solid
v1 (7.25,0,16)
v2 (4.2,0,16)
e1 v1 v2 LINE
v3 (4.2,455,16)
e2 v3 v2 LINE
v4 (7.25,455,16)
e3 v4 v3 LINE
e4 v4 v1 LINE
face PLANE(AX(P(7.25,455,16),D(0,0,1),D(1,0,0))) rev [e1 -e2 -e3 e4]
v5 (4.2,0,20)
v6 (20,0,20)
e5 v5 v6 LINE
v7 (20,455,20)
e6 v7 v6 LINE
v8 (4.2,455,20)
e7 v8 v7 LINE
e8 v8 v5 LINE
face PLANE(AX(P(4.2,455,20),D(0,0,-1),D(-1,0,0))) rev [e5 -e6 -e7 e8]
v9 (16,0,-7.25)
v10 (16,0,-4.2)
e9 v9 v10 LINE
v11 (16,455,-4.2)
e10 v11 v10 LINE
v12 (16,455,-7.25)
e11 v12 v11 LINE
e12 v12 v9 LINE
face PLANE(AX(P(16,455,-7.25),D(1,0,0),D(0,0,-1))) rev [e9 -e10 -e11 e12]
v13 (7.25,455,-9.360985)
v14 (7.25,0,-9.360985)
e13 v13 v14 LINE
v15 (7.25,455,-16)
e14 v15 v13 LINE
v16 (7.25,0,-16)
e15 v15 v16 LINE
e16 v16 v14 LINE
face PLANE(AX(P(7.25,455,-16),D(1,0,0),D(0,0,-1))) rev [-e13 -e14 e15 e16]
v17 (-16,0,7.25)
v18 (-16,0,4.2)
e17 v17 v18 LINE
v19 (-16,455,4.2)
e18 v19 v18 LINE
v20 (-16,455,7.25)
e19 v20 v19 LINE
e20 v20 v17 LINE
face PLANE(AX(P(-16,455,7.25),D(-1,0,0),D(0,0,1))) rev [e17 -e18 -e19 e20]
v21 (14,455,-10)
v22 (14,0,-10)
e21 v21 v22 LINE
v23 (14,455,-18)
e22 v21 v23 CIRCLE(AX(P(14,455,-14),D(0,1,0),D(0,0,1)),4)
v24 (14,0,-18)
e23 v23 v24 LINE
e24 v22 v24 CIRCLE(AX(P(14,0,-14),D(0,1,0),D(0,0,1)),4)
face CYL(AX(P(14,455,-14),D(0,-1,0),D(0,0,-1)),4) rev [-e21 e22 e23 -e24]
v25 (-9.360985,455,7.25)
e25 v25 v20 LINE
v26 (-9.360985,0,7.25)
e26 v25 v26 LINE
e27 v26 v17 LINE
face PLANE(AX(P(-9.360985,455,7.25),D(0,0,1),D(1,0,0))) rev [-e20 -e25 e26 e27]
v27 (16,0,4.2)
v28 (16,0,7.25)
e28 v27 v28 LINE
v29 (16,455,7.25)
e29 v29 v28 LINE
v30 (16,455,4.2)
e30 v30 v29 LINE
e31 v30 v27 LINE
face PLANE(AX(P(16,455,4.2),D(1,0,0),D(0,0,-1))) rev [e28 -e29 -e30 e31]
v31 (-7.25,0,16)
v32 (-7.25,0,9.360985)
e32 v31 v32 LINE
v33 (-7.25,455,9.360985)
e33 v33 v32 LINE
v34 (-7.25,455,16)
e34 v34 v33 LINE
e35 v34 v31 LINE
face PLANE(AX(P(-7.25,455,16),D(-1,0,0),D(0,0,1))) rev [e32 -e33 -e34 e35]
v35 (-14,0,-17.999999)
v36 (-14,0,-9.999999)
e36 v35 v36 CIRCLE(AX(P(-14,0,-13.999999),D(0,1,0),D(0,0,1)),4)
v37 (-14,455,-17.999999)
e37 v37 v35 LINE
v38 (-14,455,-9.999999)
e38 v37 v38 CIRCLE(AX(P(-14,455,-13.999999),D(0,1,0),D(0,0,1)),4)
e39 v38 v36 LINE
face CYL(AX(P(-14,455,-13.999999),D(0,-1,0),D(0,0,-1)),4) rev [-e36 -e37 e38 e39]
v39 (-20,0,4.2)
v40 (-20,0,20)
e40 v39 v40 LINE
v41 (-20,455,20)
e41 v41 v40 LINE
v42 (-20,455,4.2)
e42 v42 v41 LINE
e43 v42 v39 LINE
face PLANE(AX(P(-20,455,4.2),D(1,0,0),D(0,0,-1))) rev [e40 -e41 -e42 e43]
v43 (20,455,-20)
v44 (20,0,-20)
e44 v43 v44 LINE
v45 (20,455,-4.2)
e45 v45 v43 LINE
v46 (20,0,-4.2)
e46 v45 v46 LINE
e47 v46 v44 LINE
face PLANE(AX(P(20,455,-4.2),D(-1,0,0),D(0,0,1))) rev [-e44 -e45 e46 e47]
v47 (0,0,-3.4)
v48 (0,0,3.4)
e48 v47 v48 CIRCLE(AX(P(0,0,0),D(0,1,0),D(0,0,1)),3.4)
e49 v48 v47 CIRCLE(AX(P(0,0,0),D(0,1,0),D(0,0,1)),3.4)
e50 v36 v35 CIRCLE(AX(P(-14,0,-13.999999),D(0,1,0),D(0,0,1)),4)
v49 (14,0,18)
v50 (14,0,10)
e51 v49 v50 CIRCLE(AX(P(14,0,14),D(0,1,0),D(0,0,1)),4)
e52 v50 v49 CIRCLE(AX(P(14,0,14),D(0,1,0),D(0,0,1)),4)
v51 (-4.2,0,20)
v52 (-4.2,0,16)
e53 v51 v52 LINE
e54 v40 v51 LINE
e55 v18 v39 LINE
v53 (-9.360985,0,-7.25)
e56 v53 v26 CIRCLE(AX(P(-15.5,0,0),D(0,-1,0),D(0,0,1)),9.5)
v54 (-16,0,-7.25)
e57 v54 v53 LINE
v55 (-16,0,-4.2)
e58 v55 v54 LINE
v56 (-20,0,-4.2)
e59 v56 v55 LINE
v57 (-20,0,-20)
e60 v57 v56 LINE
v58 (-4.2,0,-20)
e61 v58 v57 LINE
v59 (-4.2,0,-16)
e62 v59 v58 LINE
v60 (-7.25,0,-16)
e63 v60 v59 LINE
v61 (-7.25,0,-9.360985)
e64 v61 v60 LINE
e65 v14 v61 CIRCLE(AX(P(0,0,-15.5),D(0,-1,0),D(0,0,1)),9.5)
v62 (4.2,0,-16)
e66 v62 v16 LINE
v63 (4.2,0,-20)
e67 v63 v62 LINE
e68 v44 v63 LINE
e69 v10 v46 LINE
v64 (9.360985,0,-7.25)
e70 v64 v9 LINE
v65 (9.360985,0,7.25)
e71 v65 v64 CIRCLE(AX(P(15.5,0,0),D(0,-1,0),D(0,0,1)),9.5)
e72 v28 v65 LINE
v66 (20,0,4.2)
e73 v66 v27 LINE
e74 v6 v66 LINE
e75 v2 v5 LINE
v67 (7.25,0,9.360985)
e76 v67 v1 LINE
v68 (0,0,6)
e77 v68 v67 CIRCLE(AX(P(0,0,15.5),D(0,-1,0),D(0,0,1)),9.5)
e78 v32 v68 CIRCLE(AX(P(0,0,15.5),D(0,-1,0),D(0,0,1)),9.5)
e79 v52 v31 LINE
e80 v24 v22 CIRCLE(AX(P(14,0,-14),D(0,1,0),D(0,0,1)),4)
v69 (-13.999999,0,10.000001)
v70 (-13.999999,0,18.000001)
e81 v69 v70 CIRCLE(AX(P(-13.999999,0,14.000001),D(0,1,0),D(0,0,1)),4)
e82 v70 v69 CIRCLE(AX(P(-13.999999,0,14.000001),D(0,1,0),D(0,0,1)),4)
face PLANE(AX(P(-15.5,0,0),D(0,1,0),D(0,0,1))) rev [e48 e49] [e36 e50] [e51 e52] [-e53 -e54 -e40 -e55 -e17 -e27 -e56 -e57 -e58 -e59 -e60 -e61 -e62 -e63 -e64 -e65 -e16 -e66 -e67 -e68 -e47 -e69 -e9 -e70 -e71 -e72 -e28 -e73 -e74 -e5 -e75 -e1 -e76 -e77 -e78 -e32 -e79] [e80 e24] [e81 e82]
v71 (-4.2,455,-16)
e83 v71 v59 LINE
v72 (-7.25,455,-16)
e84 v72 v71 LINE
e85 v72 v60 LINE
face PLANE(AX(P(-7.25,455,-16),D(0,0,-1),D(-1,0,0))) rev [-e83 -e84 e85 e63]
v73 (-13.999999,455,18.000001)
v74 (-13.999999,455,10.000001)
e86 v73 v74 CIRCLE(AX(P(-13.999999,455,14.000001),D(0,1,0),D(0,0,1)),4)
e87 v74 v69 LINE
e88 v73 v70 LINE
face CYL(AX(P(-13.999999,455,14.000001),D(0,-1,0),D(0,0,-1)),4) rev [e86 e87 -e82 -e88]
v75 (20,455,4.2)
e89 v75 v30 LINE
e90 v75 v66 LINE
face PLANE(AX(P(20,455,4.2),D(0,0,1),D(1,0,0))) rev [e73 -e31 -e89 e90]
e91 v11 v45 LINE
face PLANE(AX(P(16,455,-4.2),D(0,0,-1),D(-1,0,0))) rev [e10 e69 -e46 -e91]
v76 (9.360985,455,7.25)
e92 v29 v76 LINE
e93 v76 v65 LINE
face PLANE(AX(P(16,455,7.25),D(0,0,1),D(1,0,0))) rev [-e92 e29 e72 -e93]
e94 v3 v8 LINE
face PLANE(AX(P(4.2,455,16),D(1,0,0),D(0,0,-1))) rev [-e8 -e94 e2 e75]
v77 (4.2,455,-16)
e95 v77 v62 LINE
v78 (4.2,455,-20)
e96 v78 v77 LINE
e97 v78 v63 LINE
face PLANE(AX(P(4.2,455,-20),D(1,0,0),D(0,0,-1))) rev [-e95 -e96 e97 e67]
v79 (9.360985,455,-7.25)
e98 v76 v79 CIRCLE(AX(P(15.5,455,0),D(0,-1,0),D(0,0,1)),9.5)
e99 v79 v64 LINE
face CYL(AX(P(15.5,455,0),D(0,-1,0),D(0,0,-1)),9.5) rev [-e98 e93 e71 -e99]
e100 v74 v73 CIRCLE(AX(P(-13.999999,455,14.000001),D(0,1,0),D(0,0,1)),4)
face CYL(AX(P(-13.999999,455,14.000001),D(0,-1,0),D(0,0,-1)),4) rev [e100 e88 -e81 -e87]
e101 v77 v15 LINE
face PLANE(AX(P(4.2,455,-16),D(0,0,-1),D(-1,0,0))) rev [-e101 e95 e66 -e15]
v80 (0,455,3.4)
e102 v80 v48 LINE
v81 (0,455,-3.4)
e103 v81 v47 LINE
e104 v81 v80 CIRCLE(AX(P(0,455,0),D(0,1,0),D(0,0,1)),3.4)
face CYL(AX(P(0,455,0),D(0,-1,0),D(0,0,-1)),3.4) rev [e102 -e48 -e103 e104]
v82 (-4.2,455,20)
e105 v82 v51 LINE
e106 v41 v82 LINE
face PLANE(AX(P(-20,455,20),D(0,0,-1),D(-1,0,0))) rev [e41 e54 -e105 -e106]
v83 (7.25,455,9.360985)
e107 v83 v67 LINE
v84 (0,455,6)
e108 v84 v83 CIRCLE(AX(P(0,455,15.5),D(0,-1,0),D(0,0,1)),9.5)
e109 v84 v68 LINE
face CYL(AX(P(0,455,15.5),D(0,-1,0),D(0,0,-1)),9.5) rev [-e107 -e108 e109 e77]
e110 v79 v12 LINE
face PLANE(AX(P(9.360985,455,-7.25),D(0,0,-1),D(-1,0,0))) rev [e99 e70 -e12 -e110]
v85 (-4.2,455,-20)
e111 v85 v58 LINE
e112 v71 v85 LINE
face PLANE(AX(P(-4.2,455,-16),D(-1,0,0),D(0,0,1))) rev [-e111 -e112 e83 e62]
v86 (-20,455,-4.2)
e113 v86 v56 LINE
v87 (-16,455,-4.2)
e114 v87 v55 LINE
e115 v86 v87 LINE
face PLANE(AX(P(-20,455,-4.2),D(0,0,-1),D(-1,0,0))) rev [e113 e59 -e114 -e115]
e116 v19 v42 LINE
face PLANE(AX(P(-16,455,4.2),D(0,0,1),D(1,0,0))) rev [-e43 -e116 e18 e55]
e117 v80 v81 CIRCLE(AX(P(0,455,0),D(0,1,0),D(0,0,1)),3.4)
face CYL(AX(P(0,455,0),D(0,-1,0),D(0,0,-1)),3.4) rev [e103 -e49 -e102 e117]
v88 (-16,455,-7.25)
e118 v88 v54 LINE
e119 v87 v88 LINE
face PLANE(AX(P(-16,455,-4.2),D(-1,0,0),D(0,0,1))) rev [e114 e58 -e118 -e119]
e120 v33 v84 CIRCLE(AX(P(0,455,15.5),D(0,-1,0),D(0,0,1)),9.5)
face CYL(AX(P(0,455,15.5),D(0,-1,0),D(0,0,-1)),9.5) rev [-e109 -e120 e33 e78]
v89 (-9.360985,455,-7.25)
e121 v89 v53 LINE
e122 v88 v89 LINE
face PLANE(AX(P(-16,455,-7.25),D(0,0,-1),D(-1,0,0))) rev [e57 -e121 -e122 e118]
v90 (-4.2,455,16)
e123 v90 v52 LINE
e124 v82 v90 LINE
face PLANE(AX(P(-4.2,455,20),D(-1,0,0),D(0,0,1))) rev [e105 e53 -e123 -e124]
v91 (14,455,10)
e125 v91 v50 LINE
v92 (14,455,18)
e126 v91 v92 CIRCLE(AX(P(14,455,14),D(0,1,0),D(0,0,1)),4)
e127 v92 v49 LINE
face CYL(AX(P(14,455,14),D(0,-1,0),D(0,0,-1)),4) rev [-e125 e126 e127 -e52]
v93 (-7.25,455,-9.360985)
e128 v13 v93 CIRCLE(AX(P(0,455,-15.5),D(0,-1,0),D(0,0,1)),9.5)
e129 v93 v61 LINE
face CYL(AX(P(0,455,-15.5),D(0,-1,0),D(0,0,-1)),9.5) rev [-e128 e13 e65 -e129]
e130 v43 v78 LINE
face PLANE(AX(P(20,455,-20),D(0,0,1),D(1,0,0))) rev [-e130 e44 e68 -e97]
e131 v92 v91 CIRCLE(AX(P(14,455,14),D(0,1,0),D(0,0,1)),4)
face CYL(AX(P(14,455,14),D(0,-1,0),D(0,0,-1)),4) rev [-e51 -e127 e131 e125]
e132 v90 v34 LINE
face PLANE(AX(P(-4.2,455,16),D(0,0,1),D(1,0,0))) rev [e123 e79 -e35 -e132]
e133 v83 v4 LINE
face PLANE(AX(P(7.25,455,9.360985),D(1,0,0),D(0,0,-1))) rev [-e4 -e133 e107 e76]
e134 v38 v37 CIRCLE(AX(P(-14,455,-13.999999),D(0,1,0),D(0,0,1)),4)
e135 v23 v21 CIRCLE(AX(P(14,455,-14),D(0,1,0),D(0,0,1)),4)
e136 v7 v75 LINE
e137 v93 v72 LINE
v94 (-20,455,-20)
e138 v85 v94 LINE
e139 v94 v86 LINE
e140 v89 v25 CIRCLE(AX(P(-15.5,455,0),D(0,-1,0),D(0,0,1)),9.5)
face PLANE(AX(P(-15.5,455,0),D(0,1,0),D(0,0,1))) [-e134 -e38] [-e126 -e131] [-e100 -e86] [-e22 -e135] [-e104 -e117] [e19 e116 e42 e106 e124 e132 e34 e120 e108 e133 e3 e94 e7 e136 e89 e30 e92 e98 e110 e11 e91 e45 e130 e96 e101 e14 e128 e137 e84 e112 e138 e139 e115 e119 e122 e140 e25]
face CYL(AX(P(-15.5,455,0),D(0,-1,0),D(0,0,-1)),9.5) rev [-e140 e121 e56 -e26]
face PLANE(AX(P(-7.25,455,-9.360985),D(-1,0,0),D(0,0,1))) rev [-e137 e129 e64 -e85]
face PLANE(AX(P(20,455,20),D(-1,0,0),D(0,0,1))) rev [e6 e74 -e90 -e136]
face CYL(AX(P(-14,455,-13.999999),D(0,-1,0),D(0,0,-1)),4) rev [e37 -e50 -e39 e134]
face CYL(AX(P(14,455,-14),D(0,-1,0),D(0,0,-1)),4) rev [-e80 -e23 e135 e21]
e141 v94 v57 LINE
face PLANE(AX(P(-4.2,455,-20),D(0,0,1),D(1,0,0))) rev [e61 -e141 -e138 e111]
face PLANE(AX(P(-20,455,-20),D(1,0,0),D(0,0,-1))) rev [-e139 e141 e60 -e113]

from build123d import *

# Parameters (mm, degrees)
SKETCH_3_R     = 4
SKETCH_3_R_2   = 3.4
EF4040_1_DEPTH = 455


with BuildPart() as part:
    # 草圖3 → 東野鋁型材 EF4040(1) (new body)
    with BuildSketch(Plane(origin=(0, 0, 0), x_dir=(-1, 0, 0), z_dir=(0, 1, 0))):
        with BuildLine():
            Line((-20, -20), (-4.2, -20))
            Line((-4.2, -20), (-4.2, -16))
            Line((-4.2, -16), (-7.25, -16))
            Line((-7.25, -16), (-7.25, -9.360985421))
            ThreePointArc((-7.25, -9.360985421), (0, -6), (7.25, -9.360985421))
            Line((7.25, -9.360985421), (7.25, -16))
            Line((7.25, -16), (4.2, -16))
            Line((4.2, -16), (4.2, -20))
            Line((4.2, -20), (20, -20))
            Line((20, -20), (20, -4.2))
            Line((20, -4.2), (16, -4.2))
            Line((16, -4.2), (16, -7.25))
            Line((16, -7.25), (9.360985421, -7.25))
            ThreePointArc((9.360985421, -7.25), (6, 0), (9.360985421, 7.25))
            Line((9.360985421, 7.25), (16, 7.25))
            Line((16, 7.25), (16, 4.2))
            Line((16, 4.2), (20, 4.2))
            Line((20, 4.2), (20, 20))
            Line((20, 20), (4.2, 20))
            Line((4.2, 20), (4.2, 16))
            Line((4.2, 16), (7.25, 16))
            Line((7.25, 16), (7.25, 9.360985421))
            ThreePointArc((7.25, 9.360985421), (0, 6), (-7.25, 9.360985421))
            Line((-7.25, 9.360985421), (-7.25, 16))
            Line((-7.25, 16), (-4.2, 16))
            Line((-4.2, 16), (-4.2, 20))
            Line((-4.2, 20), (-20, 20))
            Line((-20, 20), (-20, 4.2))
            Line((-20, 4.2), (-16, 4.2))
            Line((-16, 4.2), (-16, 7.25))
            Line((-16, 7.25), (-9.360985421, 7.25))
            ThreePointArc((-9.360985421, 7.25), (-6, 0), (-9.360985421, -7.25))
            Line((-9.360985421, -7.25), (-16, -7.25))
            Line((-16, -7.25), (-16, -4.2))
            Line((-16, -4.2), (-20, -4.2))
            Line((-20, -4.2), (-20, -20))
        make_face()
        with Locations((-13.999999649, -13.999999649)):
            Circle(SKETCH_3_R, mode=Mode.SUBTRACT)
        Circle(SKETCH_3_R_2, mode=Mode.SUBTRACT)
        with Locations((14.00000014, -13.999999158)):
            Circle(SKETCH_3_R, mode=Mode.SUBTRACT)
        with Locations((-13.999999649, 14.000000351)):
            Circle(SKETCH_3_R, mode=Mode.SUBTRACT)
        with Locations((13.999999158, 14.000000842)):
            Circle(SKETCH_3_R, mode=Mode.SUBTRACT)
    extrude(amount=EF4040_1_DEPTH)


solid = part.part
